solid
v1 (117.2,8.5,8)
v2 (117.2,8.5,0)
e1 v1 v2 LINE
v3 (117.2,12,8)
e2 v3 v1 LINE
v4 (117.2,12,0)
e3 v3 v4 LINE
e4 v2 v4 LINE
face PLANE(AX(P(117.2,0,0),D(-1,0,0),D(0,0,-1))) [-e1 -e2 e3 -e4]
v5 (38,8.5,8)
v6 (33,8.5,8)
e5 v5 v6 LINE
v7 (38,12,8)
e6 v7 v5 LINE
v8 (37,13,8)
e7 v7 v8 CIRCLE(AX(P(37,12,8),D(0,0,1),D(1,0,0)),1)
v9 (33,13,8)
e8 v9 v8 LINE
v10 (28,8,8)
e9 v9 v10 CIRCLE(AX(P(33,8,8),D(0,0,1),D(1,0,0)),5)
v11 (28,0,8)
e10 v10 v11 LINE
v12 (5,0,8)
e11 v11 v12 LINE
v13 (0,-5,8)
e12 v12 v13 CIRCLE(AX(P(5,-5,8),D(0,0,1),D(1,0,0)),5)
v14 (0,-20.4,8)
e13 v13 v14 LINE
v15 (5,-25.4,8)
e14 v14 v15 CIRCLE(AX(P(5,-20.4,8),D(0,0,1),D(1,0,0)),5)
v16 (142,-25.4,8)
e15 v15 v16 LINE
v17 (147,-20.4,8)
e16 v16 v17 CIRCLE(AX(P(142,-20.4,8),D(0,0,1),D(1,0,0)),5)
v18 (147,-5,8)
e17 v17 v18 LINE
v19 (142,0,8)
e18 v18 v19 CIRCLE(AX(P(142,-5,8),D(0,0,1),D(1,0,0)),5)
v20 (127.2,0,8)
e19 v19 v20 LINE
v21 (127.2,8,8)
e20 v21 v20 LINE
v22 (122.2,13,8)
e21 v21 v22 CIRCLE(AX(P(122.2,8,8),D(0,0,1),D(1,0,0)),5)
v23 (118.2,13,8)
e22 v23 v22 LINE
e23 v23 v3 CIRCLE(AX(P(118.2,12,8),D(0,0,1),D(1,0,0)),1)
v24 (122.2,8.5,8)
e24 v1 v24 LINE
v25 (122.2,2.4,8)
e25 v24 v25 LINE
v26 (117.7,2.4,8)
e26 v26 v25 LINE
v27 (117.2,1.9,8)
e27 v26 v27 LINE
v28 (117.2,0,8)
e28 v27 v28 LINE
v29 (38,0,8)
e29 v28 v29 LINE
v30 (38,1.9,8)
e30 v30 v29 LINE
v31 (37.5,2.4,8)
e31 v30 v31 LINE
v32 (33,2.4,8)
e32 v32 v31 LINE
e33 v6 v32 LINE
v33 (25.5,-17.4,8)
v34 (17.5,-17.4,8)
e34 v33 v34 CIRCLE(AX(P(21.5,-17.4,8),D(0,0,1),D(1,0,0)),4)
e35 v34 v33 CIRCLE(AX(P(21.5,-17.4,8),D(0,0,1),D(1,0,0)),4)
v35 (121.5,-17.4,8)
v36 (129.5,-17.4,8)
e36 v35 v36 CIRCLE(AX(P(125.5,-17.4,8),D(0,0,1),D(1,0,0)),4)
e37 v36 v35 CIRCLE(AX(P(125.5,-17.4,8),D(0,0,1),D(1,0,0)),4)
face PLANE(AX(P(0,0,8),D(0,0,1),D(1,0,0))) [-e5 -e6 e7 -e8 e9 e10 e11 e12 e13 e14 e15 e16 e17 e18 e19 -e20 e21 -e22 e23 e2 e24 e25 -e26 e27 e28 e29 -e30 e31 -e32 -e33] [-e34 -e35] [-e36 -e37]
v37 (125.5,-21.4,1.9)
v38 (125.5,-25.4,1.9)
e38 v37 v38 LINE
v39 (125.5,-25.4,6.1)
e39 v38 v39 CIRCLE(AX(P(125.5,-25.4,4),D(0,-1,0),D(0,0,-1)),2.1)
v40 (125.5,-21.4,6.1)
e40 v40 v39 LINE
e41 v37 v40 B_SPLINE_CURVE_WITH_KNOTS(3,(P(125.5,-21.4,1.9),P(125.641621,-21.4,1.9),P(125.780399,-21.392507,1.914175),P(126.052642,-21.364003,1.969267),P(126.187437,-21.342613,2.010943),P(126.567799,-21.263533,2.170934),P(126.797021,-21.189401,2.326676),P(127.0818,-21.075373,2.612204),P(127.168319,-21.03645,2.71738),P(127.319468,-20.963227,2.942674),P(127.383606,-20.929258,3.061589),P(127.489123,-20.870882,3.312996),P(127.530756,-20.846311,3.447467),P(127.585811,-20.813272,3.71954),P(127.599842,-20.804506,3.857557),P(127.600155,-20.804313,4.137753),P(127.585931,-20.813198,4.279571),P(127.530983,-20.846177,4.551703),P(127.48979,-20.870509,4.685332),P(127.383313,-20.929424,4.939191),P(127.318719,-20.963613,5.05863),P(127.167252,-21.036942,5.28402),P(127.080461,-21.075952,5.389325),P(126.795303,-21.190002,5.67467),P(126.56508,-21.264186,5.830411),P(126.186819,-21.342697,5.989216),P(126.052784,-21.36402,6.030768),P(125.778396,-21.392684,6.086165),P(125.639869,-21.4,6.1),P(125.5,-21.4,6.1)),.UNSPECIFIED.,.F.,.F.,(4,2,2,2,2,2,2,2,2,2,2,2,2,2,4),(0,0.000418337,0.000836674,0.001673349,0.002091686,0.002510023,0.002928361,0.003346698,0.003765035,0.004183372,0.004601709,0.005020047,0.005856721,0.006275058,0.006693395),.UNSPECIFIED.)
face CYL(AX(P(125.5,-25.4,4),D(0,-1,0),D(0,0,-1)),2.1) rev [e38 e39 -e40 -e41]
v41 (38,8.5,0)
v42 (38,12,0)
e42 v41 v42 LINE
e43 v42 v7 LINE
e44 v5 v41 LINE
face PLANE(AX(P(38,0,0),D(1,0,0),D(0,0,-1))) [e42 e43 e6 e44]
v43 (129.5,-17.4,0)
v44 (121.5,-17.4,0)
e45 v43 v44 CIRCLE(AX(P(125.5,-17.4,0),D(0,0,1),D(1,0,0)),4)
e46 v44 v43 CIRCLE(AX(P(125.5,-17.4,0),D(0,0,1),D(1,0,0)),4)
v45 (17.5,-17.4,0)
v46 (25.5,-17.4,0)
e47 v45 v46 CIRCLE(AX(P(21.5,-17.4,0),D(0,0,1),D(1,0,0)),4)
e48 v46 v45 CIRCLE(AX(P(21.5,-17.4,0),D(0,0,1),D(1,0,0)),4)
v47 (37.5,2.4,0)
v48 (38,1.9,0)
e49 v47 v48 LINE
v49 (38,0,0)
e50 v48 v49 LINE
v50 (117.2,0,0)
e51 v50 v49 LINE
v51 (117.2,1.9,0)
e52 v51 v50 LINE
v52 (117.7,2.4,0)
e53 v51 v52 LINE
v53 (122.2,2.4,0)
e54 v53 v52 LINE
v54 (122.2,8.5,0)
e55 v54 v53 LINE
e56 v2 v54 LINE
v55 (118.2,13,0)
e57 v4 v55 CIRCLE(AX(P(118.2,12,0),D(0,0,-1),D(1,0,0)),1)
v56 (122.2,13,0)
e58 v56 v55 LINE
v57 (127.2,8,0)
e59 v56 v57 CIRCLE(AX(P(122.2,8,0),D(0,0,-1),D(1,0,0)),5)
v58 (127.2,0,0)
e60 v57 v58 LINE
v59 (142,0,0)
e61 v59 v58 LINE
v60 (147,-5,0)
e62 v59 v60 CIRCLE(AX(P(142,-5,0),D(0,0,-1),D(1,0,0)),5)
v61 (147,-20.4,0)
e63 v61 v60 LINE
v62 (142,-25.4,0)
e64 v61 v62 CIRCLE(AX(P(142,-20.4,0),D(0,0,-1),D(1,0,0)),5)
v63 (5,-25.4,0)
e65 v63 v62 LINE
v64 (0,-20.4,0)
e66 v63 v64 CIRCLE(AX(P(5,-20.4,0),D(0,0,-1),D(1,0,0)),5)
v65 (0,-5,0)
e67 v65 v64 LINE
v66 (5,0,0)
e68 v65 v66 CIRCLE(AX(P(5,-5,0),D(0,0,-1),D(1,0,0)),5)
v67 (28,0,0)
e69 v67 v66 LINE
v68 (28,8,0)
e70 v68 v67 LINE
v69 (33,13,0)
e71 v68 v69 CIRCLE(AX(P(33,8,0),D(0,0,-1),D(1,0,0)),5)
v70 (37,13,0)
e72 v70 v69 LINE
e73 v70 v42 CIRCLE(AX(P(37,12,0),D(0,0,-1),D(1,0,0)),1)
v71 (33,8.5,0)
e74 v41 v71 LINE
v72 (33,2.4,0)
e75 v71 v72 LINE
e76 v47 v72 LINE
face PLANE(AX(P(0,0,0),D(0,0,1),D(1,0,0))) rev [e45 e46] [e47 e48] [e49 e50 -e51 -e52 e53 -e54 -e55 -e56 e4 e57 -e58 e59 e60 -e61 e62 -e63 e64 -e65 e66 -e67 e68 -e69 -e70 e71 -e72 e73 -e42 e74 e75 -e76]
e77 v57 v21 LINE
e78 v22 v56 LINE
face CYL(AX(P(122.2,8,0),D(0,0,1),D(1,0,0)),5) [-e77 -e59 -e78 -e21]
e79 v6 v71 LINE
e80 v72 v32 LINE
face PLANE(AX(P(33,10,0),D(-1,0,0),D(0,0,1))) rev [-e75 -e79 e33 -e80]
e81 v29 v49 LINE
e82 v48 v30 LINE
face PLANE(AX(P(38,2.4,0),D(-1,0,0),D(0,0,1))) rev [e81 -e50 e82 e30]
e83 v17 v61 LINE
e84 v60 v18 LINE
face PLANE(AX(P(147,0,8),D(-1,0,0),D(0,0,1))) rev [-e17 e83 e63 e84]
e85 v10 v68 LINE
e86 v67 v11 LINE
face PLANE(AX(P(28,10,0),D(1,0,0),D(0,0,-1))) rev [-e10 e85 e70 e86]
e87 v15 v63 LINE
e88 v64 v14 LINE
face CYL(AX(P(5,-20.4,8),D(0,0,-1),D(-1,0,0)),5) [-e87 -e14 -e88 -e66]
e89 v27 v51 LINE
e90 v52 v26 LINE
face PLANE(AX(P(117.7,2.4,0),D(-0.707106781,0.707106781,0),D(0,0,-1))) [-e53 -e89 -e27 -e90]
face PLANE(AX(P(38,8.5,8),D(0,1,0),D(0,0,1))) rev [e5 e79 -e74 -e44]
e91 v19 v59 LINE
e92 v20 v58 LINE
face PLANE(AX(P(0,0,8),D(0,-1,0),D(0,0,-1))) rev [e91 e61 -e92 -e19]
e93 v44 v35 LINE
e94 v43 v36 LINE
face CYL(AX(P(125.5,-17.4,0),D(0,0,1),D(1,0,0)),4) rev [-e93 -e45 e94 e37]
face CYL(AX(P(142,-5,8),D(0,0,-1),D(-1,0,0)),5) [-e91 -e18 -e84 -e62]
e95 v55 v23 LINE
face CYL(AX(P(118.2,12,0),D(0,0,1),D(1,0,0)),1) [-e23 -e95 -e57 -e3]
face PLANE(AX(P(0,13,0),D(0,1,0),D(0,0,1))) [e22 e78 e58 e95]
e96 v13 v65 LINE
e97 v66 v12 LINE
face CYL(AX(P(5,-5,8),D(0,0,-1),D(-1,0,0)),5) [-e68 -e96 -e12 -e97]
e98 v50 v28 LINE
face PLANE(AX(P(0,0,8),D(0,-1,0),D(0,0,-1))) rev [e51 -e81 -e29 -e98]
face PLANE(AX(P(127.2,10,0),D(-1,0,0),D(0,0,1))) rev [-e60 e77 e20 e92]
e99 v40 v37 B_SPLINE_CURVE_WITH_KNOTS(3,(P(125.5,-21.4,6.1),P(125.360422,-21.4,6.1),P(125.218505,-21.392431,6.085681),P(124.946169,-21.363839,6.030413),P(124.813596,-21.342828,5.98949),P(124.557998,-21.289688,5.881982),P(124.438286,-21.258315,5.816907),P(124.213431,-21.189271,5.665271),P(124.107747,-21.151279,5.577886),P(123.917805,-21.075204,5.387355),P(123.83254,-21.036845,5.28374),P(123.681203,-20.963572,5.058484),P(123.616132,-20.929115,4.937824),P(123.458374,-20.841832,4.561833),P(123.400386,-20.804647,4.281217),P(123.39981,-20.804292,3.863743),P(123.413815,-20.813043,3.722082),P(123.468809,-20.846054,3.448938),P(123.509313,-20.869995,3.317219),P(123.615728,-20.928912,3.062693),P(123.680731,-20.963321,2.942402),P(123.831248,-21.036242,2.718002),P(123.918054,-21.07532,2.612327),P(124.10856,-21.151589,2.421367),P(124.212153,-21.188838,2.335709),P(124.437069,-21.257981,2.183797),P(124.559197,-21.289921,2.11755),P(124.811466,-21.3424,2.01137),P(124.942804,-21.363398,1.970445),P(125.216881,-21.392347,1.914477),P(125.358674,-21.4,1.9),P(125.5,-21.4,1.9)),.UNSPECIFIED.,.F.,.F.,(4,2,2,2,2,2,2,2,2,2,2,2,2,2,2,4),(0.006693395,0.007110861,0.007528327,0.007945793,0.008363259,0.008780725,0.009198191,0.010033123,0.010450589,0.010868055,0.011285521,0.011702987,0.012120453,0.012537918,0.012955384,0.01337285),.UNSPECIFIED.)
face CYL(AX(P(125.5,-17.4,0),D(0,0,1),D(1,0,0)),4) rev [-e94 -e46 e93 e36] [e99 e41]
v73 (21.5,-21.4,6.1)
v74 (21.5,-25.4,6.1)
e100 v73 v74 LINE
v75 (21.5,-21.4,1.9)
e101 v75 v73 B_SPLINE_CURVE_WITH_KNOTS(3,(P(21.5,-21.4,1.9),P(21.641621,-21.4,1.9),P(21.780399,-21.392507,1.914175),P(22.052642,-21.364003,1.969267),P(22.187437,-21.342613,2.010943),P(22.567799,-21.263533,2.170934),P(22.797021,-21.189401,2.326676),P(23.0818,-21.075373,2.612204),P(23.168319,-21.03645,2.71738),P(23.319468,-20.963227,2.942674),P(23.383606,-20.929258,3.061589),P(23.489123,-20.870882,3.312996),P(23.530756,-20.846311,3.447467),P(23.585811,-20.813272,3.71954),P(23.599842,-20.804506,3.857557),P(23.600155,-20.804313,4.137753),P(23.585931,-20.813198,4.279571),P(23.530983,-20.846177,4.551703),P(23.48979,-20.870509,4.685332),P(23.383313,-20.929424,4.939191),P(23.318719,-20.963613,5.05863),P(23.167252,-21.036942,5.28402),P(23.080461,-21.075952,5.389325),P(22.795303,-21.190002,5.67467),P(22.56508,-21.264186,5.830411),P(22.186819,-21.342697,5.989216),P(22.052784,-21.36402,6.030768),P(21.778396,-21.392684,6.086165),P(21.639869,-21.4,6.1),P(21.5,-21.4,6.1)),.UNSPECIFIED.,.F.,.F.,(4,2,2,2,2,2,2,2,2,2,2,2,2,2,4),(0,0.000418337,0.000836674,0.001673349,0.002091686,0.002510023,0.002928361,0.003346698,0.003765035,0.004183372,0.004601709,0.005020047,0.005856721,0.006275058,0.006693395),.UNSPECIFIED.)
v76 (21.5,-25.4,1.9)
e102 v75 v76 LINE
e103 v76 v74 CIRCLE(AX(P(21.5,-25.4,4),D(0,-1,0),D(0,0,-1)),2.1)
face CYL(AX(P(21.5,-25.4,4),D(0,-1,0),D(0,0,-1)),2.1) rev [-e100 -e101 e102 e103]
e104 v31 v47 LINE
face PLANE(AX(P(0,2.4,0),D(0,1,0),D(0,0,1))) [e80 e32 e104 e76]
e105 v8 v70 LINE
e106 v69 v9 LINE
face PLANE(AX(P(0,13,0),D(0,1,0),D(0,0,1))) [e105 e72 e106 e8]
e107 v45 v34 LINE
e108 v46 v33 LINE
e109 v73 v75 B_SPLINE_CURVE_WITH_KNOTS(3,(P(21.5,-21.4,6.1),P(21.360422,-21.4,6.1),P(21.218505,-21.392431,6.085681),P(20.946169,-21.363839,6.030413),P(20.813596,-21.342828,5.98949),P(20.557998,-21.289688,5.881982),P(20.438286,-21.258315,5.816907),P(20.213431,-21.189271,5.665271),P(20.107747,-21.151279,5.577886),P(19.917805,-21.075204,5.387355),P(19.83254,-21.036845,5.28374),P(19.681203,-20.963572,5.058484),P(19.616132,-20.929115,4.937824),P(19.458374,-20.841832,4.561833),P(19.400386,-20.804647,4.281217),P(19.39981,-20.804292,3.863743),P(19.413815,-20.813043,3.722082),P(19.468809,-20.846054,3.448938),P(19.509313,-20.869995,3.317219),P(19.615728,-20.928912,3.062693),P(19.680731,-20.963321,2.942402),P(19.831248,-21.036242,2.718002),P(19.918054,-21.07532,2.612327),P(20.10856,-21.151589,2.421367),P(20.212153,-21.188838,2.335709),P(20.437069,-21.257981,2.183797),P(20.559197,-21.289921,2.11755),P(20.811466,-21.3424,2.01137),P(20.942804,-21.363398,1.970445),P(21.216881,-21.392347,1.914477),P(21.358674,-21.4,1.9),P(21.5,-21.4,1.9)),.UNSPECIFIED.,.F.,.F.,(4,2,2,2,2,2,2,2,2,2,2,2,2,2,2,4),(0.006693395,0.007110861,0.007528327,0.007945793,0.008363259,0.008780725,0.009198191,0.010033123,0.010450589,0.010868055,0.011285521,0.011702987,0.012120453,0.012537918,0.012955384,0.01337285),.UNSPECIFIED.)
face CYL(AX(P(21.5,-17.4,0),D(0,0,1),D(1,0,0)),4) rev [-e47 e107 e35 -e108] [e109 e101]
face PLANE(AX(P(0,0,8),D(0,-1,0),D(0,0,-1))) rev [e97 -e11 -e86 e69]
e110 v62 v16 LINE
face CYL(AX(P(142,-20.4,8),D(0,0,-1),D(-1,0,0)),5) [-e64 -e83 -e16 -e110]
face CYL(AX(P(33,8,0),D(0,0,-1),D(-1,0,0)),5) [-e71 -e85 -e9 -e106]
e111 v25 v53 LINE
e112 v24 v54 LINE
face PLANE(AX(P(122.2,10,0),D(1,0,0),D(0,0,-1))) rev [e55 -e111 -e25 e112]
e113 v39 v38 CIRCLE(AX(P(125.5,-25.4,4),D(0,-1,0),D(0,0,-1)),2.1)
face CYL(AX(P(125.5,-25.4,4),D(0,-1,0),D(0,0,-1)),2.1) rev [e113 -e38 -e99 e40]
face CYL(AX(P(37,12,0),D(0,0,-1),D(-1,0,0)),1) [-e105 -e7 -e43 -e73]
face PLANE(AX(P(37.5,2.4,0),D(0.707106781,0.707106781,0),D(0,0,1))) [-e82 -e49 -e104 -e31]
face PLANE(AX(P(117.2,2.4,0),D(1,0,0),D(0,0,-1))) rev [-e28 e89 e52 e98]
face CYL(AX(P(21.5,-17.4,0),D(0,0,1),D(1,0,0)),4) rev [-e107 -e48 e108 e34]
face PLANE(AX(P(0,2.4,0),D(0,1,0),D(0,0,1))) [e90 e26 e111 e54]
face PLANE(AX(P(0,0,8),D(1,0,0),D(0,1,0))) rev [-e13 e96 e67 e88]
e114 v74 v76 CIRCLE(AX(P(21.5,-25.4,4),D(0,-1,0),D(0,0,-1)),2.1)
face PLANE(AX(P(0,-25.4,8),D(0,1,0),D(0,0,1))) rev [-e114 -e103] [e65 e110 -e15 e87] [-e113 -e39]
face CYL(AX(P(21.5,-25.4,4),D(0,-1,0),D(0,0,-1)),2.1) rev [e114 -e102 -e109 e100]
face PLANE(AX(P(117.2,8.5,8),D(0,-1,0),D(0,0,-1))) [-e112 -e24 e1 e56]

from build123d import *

# Parameters (mm, degrees)
SKETCH1_W                      = 147
SKETCH1_H                      = 25.4
BOSS_EXTRUDE1_DEPTH            = 8
SKETCH2_W                      = 5
SKETCH2_H                      = 8
BOSS_EXTRUDE2_DEPTH            = 10
SKETCH3_W                      = 8
SKETCH3_H                      = 1.5
BOSS_EXTRUDE3_DEPTH            = 5
SKETCH4_W                      = 5
SKETCH4_H                      = 8
BOSS_EXTRUDE4_DEPTH            = 2.4
SKETCH7_R                      = 4
CUT_EXTRUDE1_DEPTH             = 150.392637034
SKETCH8_W                      = 10
SKETCH8_H                      = 8
BOSS_EXTRUDE5_DEPTH            = 3
FILLET1_R                      = 5
CHAMFER1_SIZE                  = 0.5
F_4_2_4_2_DIAMETER_HOLE1_D     = 4.2
F_4_2_4_2_DIAMETER_HOLE1_DEPTH = 9.5
F_4_2_4_2_DIAMETER_HOLE1_TIP   = 1.2618073
FILLET2_R                      = 5
FILLET3_R                      = 1


with BuildPart() as part:
    # Sketch1 → Boss-Extrude1 (new body)
    with BuildSketch(Plane.XY):
        with Locations((73.5, -12.7)):
            Rectangle(SKETCH1_W, SKETCH1_H)
    extrude(amount=BOSS_EXTRUDE1_DEPTH)

    # Sketch2 → Boss-Extrude2 (add)
    with BuildSketch(Plane(origin=(0, 0, 0), x_dir=(1, 0, 0), z_dir=(0, 1, 0))):
        with Locations((124.7, -4)):
            Rectangle(SKETCH2_W, SKETCH2_H)
        with Locations((30.5, -4)):
            Rectangle(SKETCH2_W, SKETCH2_H)
    extrude(amount=BOSS_EXTRUDE2_DEPTH)

    # Sketch3 → Boss-Extrude3 (add)
    with BuildSketch(Plane(origin=(33, 0, 0), x_dir=(0, 0, -1), z_dir=(1, 0, 0))):
        with Locations((-4, 9.25)):
            Rectangle(SKETCH3_W, SKETCH3_H)
    boss_extrude3 = extrude(amount=BOSS_EXTRUDE3_DEPTH)

    # Mirror1: Boss-Extrude3 across plane
    add(boss_extrude3.mirror(Plane(origin=(77.6, 0, 0), x_dir=(0, 0, 1), z_dir=(1, 0, 0))))

    # Sketch4 → Boss-Extrude4 (add)
    with BuildSketch(Plane(origin=(0, 0, 0), x_dir=(1, 0, 0), z_dir=(0, 1, 0))):
        with Locations((35.5, -4)):
            Rectangle(SKETCH4_W, SKETCH4_H)
        with Locations((119.7, -4)):
            Rectangle(SKETCH4_W, SKETCH4_H)
    extrude(amount=BOSS_EXTRUDE4_DEPTH)

    # Sketch7 → Cut-Extrude1 (cut, through all)
    with BuildSketch(Plane.XY.offset(8)):
        with Locations((21.5, -17.4)):
            Circle(SKETCH7_R)
        with Locations((125.5, -17.4)):
            Circle(SKETCH7_R)
    extrude(amount=-CUT_EXTRUDE1_DEPTH, mode=Mode.SUBTRACT)

    # Sketch8 → Boss-Extrude5 (add)
    with BuildSketch(Plane(origin=(0, 10, 0), x_dir=(1, 0, 0), z_dir=(0, 1, 0))):
        with Locations((33, -4)):
            Rectangle(SKETCH8_W, SKETCH8_H)
        with Locations((122.2, -4)):
            Rectangle(SKETCH8_W, SKETCH8_H)
    extrude(amount=BOSS_EXTRUDE5_DEPTH)

    # Fillet1
    fillet1_edges = [part.edges().sort_by_distance(p)[0] for p in [
        (28, 13, 4),
        (127.2, 13, 4),
        (0, 0, 4),
        (147, 0, 4),
    ]]
    fillet(fillet1_edges, radius=FILLET1_R)

    # Chamfer1
    chamfer1_edges = [part.edges().sort_by_distance(p)[0] for p in [
        (38, 2.4, 4),
        (117.2, 2.4, 4),
    ]]
    chamfer(chamfer1_edges, length=CHAMFER1_SIZE)

    # Ø4.2 (4.2) Diameter Hole1
    with Locations(Plane.XZ.offset(25.4)):
        with Locations((21.5, 4), (125.5, 4)):
            Hole(F_4_2_4_2_DIAMETER_HOLE1_D / 2, depth=F_4_2_4_2_DIAMETER_HOLE1_DEPTH)
            with Locations((0, 0, -(F_4_2_4_2_DIAMETER_HOLE1_DEPTH + F_4_2_4_2_DIAMETER_HOLE1_TIP / 2))):  # 118° drill point
                Cone(0, F_4_2_4_2_DIAMETER_HOLE1_D / 2, F_4_2_4_2_DIAMETER_HOLE1_TIP, mode=Mode.SUBTRACT)

    # Fillet2
    fillet2_edges = [part.edges().sort_by_distance(p)[0] for p in [
        (147, -25.4, 4),
        (0, -25.4, 4),
    ]]
    fillet(fillet2_edges, radius=FILLET2_R)

    # Fillet3
    fillet3_edges = [part.edges().sort_by_distance(p)[0] for p in [
        (38, 13, 4),
        (117.2, 13, 4),
    ]]
    fillet(fillet3_edges, radius=FILLET3_R)


solid = part.part
